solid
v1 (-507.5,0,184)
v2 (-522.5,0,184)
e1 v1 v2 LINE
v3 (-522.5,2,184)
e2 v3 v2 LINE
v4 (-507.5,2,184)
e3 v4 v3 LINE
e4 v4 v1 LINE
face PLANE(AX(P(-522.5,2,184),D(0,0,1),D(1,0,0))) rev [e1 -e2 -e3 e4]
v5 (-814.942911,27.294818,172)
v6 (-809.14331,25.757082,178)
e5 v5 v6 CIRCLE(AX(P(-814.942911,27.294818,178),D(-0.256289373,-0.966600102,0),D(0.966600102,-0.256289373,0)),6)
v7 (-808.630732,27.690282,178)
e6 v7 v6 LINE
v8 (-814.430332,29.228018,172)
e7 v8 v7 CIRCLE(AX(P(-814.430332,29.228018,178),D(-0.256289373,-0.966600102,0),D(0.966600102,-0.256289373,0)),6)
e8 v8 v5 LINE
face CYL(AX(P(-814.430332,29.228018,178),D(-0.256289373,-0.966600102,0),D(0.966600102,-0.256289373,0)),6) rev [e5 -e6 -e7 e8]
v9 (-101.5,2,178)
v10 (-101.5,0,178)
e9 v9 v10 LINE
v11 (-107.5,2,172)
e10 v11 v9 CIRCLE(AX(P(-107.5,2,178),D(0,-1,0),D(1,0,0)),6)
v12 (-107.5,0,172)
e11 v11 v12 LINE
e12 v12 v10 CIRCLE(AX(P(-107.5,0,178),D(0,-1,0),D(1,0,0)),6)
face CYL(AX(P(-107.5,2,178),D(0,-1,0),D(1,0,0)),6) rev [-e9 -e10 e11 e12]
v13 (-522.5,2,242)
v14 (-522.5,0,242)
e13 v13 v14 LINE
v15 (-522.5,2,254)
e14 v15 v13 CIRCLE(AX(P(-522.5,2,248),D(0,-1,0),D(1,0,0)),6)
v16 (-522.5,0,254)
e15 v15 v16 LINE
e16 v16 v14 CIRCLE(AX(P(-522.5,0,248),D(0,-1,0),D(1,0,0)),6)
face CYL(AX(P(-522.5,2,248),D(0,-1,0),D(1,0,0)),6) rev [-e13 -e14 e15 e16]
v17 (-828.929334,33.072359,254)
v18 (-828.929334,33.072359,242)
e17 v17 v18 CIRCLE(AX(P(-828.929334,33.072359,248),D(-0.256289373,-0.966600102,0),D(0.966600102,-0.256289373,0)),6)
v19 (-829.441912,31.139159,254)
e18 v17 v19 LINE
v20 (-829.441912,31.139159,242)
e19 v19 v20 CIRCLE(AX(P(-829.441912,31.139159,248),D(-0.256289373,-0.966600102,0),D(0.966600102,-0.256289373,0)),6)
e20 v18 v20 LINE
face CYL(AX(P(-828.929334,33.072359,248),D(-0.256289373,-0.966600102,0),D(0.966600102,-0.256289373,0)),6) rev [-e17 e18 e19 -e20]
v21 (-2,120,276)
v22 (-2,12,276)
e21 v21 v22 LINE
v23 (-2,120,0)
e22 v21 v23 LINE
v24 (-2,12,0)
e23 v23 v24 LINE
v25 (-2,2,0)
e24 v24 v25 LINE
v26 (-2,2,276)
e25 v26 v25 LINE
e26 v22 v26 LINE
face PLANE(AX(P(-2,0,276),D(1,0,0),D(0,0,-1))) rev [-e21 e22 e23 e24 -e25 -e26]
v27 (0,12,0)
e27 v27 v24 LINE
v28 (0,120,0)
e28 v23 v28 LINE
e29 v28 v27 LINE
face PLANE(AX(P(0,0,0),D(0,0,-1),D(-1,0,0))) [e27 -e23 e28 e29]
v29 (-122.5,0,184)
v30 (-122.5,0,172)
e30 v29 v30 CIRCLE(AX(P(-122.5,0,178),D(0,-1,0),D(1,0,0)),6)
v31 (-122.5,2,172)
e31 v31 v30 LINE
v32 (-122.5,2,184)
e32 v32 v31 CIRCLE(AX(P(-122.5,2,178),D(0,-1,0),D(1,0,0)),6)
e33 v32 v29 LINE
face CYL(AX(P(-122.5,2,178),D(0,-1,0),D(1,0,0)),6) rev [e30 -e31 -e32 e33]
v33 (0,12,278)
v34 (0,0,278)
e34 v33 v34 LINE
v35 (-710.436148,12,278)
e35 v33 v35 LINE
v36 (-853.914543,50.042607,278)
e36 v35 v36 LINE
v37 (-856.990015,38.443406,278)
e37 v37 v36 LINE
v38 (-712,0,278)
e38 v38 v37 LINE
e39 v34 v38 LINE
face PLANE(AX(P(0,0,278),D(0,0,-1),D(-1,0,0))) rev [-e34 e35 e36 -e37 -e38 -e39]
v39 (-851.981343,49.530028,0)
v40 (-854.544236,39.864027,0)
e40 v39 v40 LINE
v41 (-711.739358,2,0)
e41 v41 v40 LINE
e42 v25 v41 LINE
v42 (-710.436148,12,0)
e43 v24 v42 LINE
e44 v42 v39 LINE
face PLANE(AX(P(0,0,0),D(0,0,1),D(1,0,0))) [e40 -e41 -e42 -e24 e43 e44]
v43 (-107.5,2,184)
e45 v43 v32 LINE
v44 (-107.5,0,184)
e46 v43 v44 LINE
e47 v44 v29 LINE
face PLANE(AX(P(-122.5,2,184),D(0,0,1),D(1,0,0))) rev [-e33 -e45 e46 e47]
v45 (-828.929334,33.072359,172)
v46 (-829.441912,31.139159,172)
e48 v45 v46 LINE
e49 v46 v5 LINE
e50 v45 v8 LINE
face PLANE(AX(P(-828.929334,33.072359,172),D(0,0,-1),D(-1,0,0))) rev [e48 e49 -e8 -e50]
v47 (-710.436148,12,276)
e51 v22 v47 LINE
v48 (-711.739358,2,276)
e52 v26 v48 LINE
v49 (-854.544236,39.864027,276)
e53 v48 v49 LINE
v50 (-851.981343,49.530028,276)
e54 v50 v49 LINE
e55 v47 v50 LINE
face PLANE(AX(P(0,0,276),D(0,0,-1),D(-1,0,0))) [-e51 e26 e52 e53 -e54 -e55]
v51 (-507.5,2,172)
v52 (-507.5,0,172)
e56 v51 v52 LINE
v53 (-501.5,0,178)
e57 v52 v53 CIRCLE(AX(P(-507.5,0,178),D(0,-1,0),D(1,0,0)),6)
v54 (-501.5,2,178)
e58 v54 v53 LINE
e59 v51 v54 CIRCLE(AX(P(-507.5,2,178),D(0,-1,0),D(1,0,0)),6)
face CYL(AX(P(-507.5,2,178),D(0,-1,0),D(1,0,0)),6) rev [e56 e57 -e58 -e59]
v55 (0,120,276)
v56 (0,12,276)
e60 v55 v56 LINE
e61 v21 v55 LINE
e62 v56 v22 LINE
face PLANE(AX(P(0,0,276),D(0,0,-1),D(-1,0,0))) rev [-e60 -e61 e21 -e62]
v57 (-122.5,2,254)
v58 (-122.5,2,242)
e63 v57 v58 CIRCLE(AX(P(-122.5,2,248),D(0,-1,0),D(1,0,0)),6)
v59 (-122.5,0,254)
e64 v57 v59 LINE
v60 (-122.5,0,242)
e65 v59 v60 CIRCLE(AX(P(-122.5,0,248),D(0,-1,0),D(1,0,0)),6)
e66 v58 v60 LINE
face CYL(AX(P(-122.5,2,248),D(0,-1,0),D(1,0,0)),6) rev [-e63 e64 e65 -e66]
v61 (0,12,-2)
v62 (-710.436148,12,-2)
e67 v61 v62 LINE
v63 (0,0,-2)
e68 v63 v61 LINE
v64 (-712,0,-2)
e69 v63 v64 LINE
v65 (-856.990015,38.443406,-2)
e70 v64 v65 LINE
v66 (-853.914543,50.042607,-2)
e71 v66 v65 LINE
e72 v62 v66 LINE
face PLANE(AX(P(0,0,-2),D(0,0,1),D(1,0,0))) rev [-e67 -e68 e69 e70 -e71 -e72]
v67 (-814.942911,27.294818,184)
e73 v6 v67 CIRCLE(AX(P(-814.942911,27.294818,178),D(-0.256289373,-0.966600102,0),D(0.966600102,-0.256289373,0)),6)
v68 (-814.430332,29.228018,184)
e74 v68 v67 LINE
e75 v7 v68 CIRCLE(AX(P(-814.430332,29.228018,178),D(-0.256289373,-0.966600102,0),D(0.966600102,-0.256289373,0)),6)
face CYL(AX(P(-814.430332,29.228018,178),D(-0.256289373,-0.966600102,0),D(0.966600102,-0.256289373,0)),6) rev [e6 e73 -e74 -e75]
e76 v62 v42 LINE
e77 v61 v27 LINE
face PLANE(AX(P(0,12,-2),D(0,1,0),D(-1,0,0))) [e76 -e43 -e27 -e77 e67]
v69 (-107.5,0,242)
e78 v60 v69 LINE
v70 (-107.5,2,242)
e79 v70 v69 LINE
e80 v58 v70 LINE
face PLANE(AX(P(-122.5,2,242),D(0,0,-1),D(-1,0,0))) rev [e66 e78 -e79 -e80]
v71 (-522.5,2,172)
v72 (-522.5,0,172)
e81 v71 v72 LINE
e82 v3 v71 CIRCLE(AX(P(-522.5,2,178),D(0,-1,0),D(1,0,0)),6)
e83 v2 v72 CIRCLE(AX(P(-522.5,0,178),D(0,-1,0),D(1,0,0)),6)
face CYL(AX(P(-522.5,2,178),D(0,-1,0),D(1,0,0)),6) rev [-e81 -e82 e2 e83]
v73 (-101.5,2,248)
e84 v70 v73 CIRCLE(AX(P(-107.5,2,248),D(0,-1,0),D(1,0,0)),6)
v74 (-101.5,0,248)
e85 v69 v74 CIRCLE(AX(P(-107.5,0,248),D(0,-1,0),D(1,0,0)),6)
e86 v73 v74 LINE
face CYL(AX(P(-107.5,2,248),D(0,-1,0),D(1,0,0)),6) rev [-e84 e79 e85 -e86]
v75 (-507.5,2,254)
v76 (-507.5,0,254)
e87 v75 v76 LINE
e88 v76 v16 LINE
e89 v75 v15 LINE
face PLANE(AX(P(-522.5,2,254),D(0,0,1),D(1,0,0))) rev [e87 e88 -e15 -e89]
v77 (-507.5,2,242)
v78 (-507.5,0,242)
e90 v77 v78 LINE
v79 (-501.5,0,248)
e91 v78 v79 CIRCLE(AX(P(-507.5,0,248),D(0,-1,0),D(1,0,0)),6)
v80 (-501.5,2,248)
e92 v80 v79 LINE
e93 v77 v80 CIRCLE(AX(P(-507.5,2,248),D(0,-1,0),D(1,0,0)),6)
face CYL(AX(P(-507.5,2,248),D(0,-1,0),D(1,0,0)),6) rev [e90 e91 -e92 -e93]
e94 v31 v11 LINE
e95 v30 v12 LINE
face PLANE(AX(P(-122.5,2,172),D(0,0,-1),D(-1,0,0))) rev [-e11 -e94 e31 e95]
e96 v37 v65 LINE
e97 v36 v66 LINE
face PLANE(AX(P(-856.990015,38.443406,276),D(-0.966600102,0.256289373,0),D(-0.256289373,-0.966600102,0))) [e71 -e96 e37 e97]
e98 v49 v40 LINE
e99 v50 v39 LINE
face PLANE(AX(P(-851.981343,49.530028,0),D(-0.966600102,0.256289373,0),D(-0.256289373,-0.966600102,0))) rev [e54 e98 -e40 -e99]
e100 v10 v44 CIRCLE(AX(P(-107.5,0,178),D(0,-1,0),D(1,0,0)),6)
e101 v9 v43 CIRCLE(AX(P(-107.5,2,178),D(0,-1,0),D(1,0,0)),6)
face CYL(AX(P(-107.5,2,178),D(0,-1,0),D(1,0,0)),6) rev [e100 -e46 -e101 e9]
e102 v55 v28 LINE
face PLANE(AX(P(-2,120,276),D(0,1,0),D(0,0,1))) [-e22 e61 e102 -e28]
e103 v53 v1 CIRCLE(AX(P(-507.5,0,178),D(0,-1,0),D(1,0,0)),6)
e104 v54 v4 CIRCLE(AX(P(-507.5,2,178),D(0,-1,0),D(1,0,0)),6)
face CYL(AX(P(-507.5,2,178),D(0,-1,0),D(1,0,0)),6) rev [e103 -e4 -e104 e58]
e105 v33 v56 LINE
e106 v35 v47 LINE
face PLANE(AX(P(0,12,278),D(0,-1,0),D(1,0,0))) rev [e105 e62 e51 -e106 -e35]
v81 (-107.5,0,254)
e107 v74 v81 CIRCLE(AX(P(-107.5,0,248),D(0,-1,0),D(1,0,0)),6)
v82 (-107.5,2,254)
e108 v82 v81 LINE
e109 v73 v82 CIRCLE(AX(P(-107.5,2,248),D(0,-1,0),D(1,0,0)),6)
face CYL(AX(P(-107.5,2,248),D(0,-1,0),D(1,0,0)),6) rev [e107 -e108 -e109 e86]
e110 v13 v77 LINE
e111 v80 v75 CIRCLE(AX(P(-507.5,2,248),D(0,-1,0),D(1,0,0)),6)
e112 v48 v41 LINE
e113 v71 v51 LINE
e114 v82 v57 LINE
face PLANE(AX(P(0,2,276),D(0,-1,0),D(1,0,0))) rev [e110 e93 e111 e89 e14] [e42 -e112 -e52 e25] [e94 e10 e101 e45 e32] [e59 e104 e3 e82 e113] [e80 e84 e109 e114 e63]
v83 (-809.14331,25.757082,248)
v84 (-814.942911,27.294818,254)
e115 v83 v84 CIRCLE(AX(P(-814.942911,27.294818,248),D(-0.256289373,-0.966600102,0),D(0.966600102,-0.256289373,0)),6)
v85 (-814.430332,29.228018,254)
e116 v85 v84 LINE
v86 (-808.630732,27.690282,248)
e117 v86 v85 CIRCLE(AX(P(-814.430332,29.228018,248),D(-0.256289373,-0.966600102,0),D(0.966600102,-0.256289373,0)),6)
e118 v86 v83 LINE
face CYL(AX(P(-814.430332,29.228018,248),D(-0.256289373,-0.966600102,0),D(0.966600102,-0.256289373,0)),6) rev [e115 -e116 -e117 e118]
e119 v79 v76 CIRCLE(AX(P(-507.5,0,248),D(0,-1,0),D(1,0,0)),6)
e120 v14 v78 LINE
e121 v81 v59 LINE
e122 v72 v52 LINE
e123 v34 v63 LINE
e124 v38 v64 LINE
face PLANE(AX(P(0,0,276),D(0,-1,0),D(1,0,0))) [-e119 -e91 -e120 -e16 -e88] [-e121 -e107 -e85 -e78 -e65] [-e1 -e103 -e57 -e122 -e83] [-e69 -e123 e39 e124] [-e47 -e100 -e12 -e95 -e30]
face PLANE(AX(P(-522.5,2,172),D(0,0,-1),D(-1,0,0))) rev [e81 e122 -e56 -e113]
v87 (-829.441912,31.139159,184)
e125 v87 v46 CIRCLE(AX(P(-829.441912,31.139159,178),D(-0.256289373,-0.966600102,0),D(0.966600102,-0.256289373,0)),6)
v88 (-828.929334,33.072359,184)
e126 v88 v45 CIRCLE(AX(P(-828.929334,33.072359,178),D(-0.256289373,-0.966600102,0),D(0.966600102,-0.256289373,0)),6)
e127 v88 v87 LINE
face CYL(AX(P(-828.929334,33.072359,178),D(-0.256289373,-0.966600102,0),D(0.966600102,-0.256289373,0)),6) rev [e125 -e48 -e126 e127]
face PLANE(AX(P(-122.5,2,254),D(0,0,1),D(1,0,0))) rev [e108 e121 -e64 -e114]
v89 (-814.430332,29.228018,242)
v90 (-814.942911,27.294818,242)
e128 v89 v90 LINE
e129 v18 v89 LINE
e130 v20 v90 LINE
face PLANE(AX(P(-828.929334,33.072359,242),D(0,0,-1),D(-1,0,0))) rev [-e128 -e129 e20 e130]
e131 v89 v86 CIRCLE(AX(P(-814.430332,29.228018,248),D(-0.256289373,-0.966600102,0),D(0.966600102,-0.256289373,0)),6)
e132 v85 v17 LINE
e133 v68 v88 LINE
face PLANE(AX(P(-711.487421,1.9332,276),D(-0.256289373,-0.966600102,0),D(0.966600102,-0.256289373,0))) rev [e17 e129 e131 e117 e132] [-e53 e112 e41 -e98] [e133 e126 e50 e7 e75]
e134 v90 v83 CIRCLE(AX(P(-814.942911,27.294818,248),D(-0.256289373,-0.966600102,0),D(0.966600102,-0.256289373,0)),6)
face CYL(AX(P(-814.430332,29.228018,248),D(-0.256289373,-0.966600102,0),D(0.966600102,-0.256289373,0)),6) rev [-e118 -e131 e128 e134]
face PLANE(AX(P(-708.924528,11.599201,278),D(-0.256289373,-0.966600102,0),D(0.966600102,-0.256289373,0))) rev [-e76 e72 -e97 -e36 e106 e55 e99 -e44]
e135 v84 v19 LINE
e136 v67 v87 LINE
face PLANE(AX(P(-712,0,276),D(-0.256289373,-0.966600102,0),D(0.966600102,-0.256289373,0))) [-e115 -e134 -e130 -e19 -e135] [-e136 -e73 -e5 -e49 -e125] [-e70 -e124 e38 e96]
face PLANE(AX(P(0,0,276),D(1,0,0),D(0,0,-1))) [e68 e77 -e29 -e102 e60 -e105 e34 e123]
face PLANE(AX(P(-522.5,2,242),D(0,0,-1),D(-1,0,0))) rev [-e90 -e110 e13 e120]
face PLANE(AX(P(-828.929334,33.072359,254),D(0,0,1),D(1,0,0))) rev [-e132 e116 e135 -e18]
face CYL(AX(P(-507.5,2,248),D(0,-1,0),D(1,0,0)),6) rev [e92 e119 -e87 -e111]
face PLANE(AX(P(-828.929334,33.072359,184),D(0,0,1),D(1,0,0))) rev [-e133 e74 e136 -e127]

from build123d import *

# Parameters (mm, degrees)
EXTRUDE_THIN1_DEPTH  = 276
EXTRUDE_THIN2_DEPTH  = 2
EXTRUDE_THIN3_DEPTH  = 2
CUT_EXTRUDE1_DEPTH   = 2
LPATTERN1_COUNT      = 2
LPATTERN1_PITCH      = 400
LPATTERN1_COUNT_DIR2 = 2
LPATTERN1_PITCH_DIR2 = 70
CUT_EXTRUDE2_DEPTH   = 2
LPATTERN2_COUNT      = 2
LPATTERN2_PITCH      = 70
SKETCH7_W            = 2
SKETCH7_H            = 276
BOSS_EXTRUDE1_DEPTH  = 10


with BuildPart() as part:
    # Sketch1 → Extrude-Thin1 (new body)
    with BuildSketch(Plane.XY):
        Polygon((-856.990015303, 38.44340597), (-712, 0), (0, 0), (0, 120), (-2, 120), (-2, 2), (-711.739357917, 2), (-856.477436556, 40.376606174), align=None)
    extrude(amount=EXTRUDE_THIN1_DEPTH)

    # Sketch2 → Extrude-Thin2 (add)
    with BuildSketch(Plane.XY.offset(276)):
        Polygon((0, 0), (-712, 0), (-856.990015303, 38.44340597), (-853.914542825, 50.042607194), (-710.436147504, 12), (0, 12), align=None)
    extrude(amount=EXTRUDE_THIN2_DEPTH)

    # Sketch4 → Extrude-Thin3 (add)
    with BuildSketch(Plane(origin=(0, 0, 0), x_dir=(-1, 0, 0), z_dir=(0, 0, -1))):
        Polygon((0, 0), (712, 0), (856.990015303, 38.44340597), (853.914542825, 50.042607194), (710.436147504, 12), (0, 12), align=None)
    extrude(amount=EXTRUDE_THIN3_DEPTH)

    # Sketch5 → Cut-Extrude1 (cut)
    with BuildSketch(Plane.XZ):
        with BuildLine():
            Line((-122.5, 254), (-107.5, 254))
            ThreePointArc((-107.5, 254), (-101.5, 248), (-107.5, 242))
            Line((-107.5, 242), (-122.5, 242))
            ThreePointArc((-122.5, 242), (-128.5, 248), (-122.5, 254))
        make_face()
    cut_extrude1 = extrude(amount=-CUT_EXTRUDE1_DEPTH, mode=Mode.SUBTRACT)

    # LPattern1: Cut-Extrude1 2 × 2
    with Locations(*[(-i * LPATTERN1_PITCH, 0, -j * LPATTERN1_PITCH_DIR2) for i in range(LPATTERN1_COUNT) for j in range(LPATTERN1_COUNT_DIR2) if (i, j) != (0, 0)]):
        add(cut_extrude1, mode=Mode.SUBTRACT)

    # Sketch6 → Cut-Extrude2 (cut)
    with BuildSketch(Plane(origin=(-46.76718086, -176.383285962, 0), x_dir=(0.9666001020169073, -0.2562893731329973, 0), z_dir=(-0.2562893731329973, -0.9666001020169073, 0))):
        with BuildLine():
            Line((-809.719272636, 254), (-794.719272636, 254))
            ThreePointArc((-794.719272636, 254), (-788.719272636, 248), (-794.719272636, 242))
            Line((-794.719272636, 242), (-809.719272636, 242))
            ThreePointArc((-809.719272636, 242), (-815.719272636, 248), (-809.719272636, 254))
        make_face()
    cut_extrude2 = extrude(amount=-CUT_EXTRUDE2_DEPTH, mode=Mode.SUBTRACT)

    # LPattern2: Cut-Extrude2 ×2
    with Locations(*[(0, 0, -i * LPATTERN2_PITCH) for i in range(1, LPATTERN2_COUNT)]):
        add(cut_extrude2, mode=Mode.SUBTRACT)

    # Sketch7 → Boss-Extrude1 (add)
    with BuildSketch(Plane(origin=(-46.254602114, -174.450085758, 0), x_dir=(0.9666001020169073, -0.25628937313299727, 0), z_dir=(0.25628937313299727, 0.9666001020169073, 0))):
        with Locations((-837.219272636, -138)):
            Rectangle(SKETCH7_W, SKETCH7_H)
    extrude(amount=BOSS_EXTRUDE1_DEPTH)


solid = part.part
